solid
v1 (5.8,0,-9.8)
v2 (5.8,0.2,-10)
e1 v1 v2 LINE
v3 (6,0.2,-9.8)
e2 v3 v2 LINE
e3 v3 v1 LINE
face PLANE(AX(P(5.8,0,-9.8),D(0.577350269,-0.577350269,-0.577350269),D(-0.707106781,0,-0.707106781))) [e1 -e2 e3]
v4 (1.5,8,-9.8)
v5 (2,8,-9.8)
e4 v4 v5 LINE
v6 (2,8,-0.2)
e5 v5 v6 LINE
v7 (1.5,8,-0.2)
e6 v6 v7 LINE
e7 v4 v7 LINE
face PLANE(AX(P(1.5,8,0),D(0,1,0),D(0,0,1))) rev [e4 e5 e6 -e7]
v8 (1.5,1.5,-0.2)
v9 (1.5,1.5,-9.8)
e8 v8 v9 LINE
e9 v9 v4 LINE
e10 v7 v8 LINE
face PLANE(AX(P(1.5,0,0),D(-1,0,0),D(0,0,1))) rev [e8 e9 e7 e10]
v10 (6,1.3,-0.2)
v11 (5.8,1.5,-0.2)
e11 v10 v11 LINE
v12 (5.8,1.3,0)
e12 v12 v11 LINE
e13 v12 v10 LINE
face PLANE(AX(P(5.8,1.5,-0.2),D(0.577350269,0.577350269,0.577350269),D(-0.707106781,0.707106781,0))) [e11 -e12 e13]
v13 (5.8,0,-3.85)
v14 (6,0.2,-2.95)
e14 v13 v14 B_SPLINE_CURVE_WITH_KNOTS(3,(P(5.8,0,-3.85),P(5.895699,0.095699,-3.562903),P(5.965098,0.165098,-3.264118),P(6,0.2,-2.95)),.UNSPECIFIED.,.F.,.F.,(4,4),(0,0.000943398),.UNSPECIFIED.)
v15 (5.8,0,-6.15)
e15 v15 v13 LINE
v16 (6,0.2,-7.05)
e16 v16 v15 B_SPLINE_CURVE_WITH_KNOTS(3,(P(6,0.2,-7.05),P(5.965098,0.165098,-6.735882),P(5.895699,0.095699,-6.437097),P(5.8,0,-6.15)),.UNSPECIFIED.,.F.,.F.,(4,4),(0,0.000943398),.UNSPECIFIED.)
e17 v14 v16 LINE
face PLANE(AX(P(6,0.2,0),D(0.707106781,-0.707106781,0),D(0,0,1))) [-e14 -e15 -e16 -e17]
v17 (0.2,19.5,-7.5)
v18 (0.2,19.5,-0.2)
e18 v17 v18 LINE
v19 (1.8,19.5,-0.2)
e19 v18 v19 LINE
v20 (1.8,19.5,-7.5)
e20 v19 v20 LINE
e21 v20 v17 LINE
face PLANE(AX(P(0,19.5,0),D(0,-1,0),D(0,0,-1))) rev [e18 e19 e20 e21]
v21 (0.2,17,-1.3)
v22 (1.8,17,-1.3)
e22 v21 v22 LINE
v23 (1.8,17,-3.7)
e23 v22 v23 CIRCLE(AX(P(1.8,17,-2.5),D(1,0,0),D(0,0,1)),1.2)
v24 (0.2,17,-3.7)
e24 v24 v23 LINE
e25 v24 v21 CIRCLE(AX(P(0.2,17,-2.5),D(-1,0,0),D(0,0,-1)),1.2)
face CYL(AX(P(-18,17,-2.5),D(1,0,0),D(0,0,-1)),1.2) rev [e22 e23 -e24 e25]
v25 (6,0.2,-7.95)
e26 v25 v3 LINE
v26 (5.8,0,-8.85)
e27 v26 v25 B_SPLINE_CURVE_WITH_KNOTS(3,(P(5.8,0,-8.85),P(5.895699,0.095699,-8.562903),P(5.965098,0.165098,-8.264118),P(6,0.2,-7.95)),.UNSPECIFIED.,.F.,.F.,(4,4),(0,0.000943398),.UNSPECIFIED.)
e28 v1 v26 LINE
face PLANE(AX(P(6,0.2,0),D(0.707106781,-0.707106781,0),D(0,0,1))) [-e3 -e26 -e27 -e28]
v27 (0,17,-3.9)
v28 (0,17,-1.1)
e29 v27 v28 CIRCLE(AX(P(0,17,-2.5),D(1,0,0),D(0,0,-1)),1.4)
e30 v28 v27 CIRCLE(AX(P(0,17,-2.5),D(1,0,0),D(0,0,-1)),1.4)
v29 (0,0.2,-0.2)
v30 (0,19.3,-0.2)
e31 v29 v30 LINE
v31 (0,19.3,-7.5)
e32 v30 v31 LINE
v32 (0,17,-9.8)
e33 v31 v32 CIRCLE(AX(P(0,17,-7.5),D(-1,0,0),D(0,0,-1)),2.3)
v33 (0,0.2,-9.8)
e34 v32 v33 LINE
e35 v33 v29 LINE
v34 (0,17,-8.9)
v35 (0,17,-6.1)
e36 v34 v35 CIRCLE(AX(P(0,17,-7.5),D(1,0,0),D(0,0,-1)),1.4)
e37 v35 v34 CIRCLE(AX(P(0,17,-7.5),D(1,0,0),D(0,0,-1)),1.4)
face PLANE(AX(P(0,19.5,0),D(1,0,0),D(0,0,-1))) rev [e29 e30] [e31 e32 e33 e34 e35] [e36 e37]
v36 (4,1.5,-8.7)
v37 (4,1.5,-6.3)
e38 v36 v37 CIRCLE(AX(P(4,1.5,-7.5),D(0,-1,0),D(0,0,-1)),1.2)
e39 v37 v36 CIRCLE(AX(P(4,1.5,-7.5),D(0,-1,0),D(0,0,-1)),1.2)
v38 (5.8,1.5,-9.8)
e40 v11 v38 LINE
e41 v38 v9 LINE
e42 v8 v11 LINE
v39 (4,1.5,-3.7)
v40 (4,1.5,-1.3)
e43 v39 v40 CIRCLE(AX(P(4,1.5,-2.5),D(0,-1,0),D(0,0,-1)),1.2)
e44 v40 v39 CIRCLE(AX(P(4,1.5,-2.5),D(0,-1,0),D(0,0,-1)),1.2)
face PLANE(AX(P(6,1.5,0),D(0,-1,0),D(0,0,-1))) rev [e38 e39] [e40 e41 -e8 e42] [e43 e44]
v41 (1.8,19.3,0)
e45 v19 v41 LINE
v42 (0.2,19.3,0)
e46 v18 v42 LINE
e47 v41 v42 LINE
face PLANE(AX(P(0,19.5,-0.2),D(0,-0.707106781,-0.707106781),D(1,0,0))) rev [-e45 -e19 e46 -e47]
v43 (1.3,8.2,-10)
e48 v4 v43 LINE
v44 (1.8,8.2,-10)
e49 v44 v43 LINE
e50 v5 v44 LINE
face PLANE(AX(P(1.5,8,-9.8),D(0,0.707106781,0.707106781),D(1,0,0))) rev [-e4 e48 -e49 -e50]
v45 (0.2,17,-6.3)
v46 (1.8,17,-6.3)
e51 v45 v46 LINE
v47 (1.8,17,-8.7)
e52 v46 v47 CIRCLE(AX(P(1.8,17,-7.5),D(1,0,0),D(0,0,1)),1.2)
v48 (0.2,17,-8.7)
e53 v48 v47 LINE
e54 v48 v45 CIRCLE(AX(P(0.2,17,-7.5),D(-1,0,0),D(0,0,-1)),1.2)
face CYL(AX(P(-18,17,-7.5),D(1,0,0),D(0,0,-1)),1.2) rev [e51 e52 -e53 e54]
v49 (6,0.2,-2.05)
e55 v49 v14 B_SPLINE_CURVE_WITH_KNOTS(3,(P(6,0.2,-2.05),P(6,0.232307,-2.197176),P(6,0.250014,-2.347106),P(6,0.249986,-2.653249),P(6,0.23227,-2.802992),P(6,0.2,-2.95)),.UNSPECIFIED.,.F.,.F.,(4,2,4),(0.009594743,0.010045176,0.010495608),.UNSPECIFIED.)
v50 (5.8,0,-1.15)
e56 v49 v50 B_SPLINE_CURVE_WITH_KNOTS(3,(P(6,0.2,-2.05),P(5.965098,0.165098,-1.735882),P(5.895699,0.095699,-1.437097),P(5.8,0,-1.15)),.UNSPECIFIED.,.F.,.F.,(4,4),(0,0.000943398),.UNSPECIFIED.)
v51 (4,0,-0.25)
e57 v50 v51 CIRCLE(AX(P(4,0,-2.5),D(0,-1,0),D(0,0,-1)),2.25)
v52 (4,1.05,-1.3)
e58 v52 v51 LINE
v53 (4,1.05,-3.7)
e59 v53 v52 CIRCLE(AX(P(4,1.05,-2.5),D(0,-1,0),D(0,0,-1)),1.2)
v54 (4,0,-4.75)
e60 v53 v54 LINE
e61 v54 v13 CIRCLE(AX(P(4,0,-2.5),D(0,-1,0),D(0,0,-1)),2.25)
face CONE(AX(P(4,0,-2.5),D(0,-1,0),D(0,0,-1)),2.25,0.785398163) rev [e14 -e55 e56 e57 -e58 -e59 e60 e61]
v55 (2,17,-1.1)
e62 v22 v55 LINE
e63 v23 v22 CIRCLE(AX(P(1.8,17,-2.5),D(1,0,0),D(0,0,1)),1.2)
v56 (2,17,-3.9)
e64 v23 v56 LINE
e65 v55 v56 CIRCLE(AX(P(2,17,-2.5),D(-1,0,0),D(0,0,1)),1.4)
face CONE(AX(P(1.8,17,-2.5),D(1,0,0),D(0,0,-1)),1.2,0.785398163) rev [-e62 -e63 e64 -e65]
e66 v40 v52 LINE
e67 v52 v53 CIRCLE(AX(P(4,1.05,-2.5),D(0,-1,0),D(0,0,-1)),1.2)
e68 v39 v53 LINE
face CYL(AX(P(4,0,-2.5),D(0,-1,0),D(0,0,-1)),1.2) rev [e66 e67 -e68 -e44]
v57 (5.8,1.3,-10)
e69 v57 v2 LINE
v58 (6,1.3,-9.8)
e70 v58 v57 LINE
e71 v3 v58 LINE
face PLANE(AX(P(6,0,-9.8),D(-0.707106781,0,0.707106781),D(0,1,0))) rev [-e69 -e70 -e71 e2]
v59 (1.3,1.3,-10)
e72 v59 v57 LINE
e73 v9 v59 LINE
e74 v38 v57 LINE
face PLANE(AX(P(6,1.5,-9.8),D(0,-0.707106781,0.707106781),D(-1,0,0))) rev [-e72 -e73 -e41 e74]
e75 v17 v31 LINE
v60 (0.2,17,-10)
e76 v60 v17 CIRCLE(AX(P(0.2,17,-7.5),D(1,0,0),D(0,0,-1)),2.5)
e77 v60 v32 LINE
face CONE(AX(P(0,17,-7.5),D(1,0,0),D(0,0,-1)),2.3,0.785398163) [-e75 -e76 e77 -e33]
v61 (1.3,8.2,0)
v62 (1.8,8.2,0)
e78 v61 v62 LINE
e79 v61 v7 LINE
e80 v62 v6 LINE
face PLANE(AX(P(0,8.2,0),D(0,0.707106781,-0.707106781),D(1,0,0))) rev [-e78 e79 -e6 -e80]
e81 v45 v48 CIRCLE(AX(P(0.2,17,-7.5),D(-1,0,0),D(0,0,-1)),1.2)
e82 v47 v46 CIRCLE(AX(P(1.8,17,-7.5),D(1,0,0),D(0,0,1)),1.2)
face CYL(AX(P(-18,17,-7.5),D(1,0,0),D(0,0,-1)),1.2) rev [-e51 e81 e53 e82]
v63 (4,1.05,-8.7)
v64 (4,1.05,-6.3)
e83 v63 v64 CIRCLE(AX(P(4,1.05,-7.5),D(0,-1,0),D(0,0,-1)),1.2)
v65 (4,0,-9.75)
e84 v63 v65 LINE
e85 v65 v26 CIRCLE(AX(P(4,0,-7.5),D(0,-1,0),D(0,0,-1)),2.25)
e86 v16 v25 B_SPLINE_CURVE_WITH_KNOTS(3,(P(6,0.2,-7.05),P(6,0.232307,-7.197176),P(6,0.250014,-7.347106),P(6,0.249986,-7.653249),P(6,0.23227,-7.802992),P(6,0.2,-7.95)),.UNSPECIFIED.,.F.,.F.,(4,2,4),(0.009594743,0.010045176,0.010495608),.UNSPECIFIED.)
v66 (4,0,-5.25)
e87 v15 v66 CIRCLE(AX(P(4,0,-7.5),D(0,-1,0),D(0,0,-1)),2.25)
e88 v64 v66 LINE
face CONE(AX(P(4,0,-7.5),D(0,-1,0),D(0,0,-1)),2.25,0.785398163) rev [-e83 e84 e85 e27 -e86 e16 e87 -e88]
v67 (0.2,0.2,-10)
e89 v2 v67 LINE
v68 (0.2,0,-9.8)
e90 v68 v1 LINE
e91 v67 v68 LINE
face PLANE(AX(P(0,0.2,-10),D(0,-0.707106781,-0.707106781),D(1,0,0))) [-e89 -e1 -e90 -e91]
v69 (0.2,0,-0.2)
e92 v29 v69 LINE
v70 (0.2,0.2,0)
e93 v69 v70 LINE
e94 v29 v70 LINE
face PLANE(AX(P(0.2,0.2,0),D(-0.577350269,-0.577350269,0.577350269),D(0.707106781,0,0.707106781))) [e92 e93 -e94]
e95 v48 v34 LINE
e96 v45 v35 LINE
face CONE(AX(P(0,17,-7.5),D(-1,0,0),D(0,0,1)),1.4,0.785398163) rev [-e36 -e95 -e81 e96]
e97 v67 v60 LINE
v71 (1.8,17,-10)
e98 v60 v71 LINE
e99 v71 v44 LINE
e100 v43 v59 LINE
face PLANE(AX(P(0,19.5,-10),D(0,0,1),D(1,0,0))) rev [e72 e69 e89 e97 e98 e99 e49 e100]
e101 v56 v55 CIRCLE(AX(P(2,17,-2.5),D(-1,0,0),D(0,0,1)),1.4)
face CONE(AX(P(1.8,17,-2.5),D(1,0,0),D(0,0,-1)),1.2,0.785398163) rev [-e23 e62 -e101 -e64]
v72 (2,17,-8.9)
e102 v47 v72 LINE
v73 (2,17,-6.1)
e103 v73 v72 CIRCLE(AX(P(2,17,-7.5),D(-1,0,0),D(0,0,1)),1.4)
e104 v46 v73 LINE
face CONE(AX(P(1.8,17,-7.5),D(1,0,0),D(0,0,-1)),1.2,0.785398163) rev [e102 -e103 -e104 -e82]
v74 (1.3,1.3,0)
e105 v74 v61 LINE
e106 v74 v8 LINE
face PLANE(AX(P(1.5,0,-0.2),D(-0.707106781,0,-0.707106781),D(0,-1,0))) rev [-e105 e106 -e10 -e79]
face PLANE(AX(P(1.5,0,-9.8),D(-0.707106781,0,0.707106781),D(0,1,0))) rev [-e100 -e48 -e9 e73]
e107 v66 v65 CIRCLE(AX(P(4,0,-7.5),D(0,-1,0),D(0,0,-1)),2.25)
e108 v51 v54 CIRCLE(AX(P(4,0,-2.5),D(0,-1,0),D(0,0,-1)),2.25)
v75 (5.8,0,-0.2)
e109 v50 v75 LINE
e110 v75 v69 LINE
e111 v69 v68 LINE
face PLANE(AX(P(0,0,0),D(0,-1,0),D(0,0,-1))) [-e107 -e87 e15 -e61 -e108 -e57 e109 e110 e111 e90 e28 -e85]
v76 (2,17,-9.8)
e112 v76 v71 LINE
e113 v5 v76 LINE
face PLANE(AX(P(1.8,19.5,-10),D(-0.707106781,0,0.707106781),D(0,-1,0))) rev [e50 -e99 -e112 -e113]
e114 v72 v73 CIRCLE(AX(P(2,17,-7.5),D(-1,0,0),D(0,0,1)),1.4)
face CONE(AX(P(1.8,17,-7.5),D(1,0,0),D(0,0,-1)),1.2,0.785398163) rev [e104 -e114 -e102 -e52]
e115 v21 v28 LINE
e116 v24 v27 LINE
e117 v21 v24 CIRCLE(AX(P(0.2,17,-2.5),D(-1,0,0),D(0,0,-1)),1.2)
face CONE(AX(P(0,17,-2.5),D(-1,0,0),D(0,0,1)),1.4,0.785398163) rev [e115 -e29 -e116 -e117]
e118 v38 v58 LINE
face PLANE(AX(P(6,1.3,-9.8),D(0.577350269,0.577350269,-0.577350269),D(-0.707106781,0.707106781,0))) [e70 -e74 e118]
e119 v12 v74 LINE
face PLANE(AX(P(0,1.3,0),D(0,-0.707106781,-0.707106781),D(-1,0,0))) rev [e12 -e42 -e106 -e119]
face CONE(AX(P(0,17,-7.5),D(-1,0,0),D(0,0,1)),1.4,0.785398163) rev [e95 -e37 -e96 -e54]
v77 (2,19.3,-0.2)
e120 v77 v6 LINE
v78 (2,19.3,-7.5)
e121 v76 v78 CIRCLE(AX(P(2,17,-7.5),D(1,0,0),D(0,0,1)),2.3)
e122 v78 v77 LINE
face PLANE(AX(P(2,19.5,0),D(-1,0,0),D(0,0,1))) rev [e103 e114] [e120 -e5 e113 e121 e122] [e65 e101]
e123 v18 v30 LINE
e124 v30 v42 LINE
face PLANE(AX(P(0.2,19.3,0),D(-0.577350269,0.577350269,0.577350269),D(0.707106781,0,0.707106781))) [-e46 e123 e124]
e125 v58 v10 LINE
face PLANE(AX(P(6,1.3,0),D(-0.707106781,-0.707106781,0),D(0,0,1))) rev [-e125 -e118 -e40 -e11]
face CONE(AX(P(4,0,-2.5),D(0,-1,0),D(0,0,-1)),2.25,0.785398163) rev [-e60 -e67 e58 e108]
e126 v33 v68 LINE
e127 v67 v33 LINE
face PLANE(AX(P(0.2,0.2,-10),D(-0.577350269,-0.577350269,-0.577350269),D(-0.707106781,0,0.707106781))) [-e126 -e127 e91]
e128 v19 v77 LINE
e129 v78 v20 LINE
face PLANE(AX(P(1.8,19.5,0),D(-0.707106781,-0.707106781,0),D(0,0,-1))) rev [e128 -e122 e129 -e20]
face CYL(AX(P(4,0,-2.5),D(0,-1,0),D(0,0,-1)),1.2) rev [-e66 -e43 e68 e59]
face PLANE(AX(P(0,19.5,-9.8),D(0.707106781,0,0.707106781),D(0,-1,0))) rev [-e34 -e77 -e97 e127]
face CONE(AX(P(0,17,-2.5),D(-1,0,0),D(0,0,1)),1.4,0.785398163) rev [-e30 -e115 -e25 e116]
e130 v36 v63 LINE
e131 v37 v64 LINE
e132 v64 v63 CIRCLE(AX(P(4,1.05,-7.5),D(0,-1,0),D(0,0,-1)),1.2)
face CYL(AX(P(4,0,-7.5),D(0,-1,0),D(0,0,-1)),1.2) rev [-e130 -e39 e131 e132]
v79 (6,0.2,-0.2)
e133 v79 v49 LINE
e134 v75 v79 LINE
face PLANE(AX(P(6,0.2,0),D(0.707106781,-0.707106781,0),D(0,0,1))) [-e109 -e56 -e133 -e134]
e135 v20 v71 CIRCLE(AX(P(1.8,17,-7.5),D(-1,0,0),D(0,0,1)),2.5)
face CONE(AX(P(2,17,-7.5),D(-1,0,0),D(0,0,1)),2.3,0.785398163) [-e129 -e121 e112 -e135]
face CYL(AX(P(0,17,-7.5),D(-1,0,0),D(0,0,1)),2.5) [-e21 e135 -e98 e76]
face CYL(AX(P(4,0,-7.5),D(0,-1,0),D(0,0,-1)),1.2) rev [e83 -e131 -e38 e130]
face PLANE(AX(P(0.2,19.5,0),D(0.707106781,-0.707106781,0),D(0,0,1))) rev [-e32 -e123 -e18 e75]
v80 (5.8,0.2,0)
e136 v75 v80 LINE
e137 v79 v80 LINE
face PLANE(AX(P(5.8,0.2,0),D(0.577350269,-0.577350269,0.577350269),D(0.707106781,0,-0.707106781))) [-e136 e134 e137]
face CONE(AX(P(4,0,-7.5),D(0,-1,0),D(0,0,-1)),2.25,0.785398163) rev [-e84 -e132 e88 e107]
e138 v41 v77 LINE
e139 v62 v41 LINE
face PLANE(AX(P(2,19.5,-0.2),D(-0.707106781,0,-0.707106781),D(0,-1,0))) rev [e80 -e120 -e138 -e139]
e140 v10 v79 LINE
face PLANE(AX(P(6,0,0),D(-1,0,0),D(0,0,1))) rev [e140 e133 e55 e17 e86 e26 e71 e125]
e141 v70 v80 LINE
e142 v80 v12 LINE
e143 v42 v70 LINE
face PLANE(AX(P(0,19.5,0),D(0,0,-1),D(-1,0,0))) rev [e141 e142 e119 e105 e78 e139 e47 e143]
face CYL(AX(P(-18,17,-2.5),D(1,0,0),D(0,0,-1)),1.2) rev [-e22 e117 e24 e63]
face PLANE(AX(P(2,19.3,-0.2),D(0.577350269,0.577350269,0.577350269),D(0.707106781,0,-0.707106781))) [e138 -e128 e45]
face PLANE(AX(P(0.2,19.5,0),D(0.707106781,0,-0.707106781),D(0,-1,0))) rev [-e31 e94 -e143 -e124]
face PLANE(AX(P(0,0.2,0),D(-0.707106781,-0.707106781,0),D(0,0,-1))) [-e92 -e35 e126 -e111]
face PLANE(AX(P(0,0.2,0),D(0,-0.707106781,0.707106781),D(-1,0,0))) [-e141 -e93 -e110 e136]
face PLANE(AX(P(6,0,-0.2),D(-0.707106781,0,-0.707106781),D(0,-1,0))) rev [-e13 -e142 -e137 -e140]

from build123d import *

# Parameters (mm, degrees)
SKETCH1_W                                    = 2
SKETCH1_H                                    = 10
BOSS_EXTRUDE1_DEPTH                          = 19.5
SKETCH2_R                                    = 1.2
CUT_EXTRUDE1_DEPTH                           = 20
SKETCH3_W                                    = 10
SKETCH3_H                                    = 1.5
BOSS_EXTRUDE2_DEPTH                          = 4
SKETCH4_W                                    = 10
SKETCH4_H                                    = 6.5
CUT_EXTRUDE2_DEPTH                           = 0.5
HOLE_SIZE_SLOTTED_COUNTERSUNK_WOOD_S_2_COUNT = 2
HOLE_SIZE_SLOTTED_COUNTERSUNK_WOOD_S_2_PITCH = 5
FILLET1_R                                    = 2.5
CHAMFER1_SIZE                                = 0.2


with BuildPart() as part:
    # Sketch1 → Boss-Extrude1 (new body)
    with BuildSketch(Plane(origin=(0, 0, 0), x_dir=(1, 0, 0), z_dir=(0, 1, 0))):
        with Locations((1, 5)):
            Rectangle(SKETCH1_W, SKETCH1_H)
    extrude(amount=BOSS_EXTRUDE1_DEPTH)

    # Sketch2 → Cut-Extrude1 (cut)
    with BuildSketch(Plane(origin=(2, 0, 0), x_dir=(0, 0, -1), z_dir=(1, 0, 0))):
        with Locations((2.5, 17)):
            Circle(SKETCH2_R)
        with Locations((7.5, 17)):
            Circle(SKETCH2_R)
    extrude(amount=-CUT_EXTRUDE1_DEPTH, mode=Mode.SUBTRACT)

    # Sketch3 → Boss-Extrude2 (add)
    with BuildSketch(Plane(origin=(2, 0, 0), x_dir=(0, 0, -1), z_dir=(1, 0, 0))):
        with Locations((5, 0.75)):
            Rectangle(SKETCH3_W, SKETCH3_H)
    extrude(amount=BOSS_EXTRUDE2_DEPTH)

    # Sketch4 → Cut-Extrude2 (cut)
    with BuildSketch(Plane(origin=(2, 0, 0), x_dir=(0, 0, -1), z_dir=(1, 0, 0))):
        with Locations((5, 4.75)):
            Rectangle(SKETCH4_W, SKETCH4_H)
    extrude(amount=-CUT_EXTRUDE2_DEPTH, mode=Mode.SUBTRACT)

    # Sketch6 → Hole size slotted countersunk wood screw type 0 (revolve, cut)
    with BuildSketch(Plane(origin=(4, 0, -2.5), x_dir=(0, 0, -1), z_dir=(1, 0, 0))):
        Polygon((0, 0), (0, 1.5), (1.2, 1.5), (1.2, 1.05), (2.25, 0), align=None)
    hole_size_slotted_countersunk_wood_screw = revolve(axis=Axis((4, -6.35, -2.5), (0, 1, 0)), mode=Mode.SUBTRACT)

    # Hole size slotted countersunk wood s 2: Hole size slotted countersunk wood screw type 0 ×2
    with Locations(*[(0, 0, -i * HOLE_SIZE_SLOTTED_COUNTERSUNK_WOOD_S_2_PITCH) for i in range(1, HOLE_SIZE_SLOTTED_COUNTERSUNK_WOOD_S_2_COUNT)]):
        add(hole_size_slotted_countersunk_wood_screw, mode=Mode.SUBTRACT)

    # Fillet1
    fillet1_edges = [part.edges().sort_by_distance(p)[0] for p in [
        (1, 19.5, -10),
    ]]
    fillet(fillet1_edges, radius=FILLET1_R)

    # Chamfer1
    chamfer1_edges = [part.edges().sort_by_distance(p)[0] for p in [
        (0, 17, -6.3),
        (0, 17, -1.3),
        (6, 0, -5),
        (2, 19.5, -3.75),
        (2, 18.767766953, -9.267766953),
        (3, 0, -10),
        (6, 0, -9.265388203),
        (6, 0.75, -10),
        (2, 12.5, -10),
        (1.75, 8, -10),
        (1.5, 4.75, -10),
        (3.75, 1.5, -10),
        (3.75, 1.5, 0),
        (1.5, 4.75, 0),
        (1.75, 8, 0),
        (2, 13.75, 0),
        (1, 19.5, 0),
        (0, 9.75, 0),
        (0, 19.5, -3.75),
        (0, 18.767766953, -9.267766953),
        (0, 8.5, -10),
        (0, 0, -5),
        (3, 0, 0),
        (6, 0, -0.734611797),
        (6, 0.75, 0),
        (6, 1.5, -5),
        (2, 17, -1.3),
        (2, 17, -6.3),
    ]]
    chamfer(chamfer1_edges, length=CHAMFER1_SIZE)


solid = part.part
